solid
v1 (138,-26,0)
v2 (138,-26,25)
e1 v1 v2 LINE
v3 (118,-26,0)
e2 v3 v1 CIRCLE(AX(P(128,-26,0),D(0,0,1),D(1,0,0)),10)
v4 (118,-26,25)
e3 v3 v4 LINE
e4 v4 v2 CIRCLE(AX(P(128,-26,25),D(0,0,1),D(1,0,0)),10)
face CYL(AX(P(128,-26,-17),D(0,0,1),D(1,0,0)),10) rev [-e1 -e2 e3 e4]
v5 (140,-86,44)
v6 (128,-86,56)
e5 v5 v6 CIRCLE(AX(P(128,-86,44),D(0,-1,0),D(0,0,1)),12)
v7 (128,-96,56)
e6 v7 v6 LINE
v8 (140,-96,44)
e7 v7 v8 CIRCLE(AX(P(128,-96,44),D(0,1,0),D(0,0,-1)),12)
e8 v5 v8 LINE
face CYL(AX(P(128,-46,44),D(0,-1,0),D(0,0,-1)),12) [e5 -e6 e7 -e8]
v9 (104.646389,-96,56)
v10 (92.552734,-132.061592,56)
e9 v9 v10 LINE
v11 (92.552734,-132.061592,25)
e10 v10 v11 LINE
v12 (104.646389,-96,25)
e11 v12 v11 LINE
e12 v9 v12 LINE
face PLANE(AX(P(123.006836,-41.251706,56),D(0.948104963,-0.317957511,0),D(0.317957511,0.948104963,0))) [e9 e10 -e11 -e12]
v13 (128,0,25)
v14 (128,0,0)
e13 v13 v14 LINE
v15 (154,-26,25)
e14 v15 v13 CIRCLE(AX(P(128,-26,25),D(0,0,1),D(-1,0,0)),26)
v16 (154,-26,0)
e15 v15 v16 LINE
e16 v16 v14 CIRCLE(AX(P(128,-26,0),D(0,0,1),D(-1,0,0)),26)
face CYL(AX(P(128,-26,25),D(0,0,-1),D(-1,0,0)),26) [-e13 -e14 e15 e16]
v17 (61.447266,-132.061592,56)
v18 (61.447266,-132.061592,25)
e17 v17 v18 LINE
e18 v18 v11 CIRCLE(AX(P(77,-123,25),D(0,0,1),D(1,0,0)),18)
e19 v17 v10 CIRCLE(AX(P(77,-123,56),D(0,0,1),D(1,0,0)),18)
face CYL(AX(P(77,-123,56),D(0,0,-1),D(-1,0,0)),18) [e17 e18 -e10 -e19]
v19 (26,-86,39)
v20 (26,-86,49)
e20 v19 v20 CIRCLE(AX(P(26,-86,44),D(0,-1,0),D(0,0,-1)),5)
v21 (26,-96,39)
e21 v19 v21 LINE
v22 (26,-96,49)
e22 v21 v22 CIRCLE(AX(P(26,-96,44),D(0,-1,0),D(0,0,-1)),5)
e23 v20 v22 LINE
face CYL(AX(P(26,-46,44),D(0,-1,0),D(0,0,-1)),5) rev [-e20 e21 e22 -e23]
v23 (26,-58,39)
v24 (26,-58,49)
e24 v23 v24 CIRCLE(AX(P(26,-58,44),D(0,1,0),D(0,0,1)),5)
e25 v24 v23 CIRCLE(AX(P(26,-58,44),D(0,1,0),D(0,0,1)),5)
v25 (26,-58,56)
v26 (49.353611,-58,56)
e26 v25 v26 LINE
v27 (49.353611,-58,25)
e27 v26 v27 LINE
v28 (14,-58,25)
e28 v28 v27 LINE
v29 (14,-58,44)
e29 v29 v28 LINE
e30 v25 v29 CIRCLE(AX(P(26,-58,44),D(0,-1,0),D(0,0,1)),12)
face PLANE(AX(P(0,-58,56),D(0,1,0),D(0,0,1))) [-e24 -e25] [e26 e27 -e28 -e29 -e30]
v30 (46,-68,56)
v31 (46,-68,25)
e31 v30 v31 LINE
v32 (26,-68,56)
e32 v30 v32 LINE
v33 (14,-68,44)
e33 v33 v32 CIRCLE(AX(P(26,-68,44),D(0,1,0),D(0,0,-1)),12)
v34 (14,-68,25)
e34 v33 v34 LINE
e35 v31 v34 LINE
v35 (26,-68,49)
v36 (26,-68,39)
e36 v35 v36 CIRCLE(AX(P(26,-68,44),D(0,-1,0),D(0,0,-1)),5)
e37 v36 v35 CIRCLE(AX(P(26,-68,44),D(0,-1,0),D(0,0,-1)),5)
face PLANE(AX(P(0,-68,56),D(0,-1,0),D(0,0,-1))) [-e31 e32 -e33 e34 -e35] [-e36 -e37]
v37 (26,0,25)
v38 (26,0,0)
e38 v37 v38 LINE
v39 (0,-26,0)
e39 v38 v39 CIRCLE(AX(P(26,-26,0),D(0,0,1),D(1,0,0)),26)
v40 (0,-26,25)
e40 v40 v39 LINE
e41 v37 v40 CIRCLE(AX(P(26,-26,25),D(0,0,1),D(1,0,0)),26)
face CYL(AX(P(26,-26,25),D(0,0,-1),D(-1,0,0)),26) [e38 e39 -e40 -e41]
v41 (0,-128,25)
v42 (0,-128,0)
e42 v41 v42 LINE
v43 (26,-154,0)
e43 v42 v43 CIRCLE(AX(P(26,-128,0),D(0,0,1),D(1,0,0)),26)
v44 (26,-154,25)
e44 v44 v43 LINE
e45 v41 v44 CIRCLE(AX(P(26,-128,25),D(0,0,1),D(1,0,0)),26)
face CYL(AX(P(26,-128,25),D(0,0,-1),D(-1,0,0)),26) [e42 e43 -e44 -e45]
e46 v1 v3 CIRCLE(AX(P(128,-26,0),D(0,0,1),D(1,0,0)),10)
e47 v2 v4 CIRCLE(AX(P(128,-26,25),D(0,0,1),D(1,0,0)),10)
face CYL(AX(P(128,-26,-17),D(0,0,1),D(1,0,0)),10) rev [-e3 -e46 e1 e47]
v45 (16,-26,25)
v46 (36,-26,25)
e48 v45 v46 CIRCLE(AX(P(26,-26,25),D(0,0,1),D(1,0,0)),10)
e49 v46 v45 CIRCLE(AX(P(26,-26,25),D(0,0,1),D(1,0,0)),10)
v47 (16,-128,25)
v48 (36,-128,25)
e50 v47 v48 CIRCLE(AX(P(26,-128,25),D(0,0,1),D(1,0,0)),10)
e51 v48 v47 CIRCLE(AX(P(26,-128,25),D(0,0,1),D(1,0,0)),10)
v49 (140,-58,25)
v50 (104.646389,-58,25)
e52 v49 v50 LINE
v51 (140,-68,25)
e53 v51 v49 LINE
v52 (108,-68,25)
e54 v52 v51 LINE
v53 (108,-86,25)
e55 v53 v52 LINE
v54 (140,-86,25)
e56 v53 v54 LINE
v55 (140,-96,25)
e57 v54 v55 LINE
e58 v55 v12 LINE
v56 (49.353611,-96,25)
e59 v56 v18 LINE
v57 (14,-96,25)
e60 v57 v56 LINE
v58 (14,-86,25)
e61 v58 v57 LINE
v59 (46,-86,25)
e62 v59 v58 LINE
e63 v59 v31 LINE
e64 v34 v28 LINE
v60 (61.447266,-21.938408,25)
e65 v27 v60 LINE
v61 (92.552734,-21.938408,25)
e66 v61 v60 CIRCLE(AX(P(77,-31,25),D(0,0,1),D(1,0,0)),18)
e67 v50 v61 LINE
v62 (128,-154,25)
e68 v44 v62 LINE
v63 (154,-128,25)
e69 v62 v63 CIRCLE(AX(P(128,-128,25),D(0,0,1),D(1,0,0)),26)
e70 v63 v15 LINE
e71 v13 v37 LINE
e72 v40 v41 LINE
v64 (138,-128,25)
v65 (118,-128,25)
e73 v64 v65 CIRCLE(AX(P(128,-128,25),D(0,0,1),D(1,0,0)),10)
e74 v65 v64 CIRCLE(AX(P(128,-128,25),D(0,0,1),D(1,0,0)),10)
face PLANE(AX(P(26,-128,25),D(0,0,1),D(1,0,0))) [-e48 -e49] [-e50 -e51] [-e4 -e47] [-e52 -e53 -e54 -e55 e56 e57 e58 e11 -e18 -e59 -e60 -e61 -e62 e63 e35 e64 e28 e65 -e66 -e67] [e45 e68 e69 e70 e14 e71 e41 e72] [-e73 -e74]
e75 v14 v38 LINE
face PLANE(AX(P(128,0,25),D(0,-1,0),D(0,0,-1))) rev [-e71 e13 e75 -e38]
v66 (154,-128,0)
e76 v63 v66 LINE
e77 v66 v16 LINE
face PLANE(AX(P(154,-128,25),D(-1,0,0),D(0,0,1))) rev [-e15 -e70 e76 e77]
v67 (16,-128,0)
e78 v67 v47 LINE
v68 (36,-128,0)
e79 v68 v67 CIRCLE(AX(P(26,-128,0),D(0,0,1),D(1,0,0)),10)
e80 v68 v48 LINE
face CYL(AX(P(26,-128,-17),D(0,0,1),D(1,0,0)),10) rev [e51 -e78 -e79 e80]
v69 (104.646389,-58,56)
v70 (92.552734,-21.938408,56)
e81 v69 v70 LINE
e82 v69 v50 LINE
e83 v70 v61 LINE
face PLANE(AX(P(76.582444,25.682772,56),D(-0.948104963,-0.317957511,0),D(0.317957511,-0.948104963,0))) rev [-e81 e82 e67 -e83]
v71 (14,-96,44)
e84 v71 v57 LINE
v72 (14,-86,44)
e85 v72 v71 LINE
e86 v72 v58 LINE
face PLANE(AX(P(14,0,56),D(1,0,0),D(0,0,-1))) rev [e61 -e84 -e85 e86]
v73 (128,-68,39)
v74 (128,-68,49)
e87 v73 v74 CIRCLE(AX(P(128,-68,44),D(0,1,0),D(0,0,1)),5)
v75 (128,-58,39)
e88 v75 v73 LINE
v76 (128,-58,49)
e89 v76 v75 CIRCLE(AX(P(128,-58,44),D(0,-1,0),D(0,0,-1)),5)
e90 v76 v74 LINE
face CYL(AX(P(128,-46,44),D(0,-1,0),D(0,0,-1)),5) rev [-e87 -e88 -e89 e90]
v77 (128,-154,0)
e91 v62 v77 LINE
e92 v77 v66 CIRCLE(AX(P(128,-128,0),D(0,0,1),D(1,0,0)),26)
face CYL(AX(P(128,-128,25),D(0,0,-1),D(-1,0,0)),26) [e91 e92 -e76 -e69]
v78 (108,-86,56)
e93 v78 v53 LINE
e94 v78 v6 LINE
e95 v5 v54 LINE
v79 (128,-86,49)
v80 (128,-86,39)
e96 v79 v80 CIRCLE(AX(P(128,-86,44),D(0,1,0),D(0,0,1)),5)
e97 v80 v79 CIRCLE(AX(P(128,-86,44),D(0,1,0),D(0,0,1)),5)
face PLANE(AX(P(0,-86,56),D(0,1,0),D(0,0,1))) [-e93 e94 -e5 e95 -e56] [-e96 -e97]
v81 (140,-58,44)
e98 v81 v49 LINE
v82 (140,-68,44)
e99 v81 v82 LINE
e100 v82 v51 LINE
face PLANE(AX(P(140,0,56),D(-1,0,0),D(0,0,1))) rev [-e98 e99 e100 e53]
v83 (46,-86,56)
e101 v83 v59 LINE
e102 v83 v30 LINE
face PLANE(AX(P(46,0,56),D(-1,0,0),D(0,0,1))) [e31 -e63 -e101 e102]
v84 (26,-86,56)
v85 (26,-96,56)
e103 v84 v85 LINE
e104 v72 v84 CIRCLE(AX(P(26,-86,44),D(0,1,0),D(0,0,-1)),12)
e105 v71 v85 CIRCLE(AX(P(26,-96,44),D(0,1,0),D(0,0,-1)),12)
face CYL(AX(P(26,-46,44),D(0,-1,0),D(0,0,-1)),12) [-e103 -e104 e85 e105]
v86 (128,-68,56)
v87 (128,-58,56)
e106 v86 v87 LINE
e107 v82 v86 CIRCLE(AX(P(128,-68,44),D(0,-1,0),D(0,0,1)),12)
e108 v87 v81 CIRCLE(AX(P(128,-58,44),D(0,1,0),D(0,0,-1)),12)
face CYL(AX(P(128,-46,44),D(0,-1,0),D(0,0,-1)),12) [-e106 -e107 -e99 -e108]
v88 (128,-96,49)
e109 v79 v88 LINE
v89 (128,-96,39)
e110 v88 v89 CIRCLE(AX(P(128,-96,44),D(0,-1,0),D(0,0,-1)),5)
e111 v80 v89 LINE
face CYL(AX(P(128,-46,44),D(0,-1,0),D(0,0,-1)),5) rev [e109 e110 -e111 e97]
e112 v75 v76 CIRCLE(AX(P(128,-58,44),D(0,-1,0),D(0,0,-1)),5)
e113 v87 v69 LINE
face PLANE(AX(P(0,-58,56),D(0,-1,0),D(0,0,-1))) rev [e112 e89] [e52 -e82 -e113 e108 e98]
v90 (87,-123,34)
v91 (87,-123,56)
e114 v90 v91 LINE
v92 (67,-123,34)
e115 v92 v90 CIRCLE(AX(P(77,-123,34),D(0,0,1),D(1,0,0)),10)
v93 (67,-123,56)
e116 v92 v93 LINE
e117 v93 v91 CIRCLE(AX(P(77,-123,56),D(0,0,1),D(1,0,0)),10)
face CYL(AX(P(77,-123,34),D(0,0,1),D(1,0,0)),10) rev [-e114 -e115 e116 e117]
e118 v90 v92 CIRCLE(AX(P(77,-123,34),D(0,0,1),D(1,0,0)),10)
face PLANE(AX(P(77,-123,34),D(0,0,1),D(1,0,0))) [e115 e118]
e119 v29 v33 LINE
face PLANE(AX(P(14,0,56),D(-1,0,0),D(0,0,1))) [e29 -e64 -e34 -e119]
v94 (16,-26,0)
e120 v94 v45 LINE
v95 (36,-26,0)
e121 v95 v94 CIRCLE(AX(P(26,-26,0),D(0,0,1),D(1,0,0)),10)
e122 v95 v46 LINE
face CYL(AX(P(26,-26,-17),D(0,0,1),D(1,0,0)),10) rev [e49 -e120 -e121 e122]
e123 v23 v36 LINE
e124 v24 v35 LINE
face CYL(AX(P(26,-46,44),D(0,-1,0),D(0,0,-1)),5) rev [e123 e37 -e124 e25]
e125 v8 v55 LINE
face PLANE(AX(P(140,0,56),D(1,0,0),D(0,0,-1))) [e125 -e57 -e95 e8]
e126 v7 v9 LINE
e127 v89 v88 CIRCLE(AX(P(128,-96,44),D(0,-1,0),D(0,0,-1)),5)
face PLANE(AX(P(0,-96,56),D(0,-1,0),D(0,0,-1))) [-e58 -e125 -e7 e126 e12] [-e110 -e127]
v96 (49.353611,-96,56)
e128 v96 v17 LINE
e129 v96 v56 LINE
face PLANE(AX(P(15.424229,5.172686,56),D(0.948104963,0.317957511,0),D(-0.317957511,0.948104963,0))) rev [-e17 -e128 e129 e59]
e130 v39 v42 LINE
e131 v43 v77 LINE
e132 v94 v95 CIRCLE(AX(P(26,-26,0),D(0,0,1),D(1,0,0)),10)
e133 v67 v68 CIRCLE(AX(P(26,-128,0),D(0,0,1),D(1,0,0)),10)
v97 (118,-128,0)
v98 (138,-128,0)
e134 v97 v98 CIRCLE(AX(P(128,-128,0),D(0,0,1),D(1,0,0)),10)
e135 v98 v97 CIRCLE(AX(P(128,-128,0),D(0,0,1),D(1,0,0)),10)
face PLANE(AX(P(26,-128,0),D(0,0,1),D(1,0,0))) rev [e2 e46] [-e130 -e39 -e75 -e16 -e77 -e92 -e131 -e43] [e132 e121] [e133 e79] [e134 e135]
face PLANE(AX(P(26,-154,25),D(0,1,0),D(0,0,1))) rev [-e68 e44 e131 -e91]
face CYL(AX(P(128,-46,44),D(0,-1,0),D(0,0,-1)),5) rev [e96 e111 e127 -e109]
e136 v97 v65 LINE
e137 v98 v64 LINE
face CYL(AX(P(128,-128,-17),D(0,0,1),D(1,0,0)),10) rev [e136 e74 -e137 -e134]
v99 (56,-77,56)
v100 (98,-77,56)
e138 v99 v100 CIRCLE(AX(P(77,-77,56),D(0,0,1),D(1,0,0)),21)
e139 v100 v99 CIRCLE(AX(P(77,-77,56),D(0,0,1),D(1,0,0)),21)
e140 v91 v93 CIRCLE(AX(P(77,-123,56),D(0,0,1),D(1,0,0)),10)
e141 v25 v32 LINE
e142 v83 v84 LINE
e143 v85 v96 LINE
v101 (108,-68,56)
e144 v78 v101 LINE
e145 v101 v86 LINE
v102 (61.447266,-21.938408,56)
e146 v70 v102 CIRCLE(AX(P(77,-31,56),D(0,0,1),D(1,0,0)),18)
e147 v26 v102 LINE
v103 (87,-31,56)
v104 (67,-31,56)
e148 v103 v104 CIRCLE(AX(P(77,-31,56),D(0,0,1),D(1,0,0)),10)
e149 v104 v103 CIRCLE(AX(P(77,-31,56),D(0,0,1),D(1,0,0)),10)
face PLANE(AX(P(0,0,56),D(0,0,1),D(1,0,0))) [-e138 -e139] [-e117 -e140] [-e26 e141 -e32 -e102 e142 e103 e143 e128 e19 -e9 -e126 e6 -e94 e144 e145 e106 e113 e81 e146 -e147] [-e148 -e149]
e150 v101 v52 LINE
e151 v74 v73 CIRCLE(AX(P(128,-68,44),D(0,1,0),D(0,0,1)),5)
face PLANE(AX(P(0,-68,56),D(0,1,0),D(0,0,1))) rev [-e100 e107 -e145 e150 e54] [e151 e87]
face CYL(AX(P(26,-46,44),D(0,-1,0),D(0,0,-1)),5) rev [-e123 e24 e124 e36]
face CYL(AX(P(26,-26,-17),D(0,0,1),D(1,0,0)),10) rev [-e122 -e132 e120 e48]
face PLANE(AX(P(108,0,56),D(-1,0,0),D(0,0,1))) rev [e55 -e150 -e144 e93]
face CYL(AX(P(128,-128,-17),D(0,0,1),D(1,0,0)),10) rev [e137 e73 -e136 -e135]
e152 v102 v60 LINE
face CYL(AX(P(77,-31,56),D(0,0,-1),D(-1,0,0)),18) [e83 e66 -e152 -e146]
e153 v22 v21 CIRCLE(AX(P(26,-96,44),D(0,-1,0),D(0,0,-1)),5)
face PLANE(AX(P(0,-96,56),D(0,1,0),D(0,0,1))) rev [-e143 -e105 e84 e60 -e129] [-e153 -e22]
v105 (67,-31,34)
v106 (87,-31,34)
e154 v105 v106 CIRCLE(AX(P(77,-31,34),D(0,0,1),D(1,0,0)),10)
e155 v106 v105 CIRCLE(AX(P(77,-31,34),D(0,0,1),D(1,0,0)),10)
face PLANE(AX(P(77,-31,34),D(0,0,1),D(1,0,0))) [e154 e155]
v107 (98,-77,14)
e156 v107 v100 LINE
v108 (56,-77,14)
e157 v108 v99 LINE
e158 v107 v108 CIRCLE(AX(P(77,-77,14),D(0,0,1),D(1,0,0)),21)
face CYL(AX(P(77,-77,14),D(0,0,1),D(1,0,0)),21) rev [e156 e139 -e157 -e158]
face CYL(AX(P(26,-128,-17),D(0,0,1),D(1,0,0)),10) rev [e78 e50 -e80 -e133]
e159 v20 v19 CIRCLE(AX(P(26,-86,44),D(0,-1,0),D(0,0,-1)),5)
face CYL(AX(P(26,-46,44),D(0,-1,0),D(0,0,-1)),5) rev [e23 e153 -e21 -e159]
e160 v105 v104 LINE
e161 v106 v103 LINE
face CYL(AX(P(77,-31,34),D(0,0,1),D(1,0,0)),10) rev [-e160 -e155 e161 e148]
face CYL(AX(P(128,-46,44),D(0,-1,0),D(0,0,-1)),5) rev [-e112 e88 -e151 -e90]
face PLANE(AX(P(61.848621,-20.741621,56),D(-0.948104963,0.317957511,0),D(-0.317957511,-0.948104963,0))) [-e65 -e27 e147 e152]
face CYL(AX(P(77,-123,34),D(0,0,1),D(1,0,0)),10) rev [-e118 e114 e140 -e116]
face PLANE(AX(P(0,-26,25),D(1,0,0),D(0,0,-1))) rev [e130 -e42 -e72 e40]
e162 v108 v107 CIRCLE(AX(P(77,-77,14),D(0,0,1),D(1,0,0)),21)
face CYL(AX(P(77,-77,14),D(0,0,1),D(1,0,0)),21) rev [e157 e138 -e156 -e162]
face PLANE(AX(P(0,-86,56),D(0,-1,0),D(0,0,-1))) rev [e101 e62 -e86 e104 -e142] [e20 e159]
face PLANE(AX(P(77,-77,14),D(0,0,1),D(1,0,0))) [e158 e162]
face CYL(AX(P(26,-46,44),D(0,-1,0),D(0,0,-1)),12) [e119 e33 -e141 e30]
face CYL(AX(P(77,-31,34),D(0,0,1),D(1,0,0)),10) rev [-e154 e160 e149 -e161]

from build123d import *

# Parameters (mm, degrees)
BASE_PLATE_DEPTH         = 25
FLANGE_BOSS_DEPTH        = 31
LUG_SLOT_1_DEPTH         = 50
LUG_SLOT_2_DEPTH         = 50
LUG_PIN_HOLES_SKETCH_R   = 5
LUG_PIN_HOLES_2X_DEPTH   = 50
FLANGE_HOLES_SKETCH_R    = 10
FLANGE_HOLES_2X_DEPTH    = 22
CENTRE_BORE_SKETCH_R     = 21
CENTRE_BORE_42_DEPTH     = 42
CORNER_HOLES_SKETCH_R    = 10
CORNER_HOLES_4X_20_DEPTH = 42


with BuildPart() as part:
    # Base Plate Sketch → Base Plate (new body)
    with BuildSketch(Plane.XY):
        with BuildLine():
            Line((0, -26), (0, -128))
            ThreePointArc((0, -128), (7.615223689, -146.384776311), (26, -154))
            Line((26, -154), (128, -154))
            ThreePointArc((128, -154), (146.384776311, -146.384776311), (154, -128))
            Line((154, -128), (154, -26))
            ThreePointArc((154, -26), (146.384776311, -7.615223689), (128, 0))
            Line((128, 0), (26, 0))
            ThreePointArc((26, 0), (7.615223689, -7.615223689), (0, -26))
        make_face()
    extrude(amount=BASE_PLATE_DEPTH)

    # Flange Boss Sketch → Flange Boss (add)
    with BuildSketch(Plane.XY.offset(25)):
        with BuildLine():
            Line((14, -96), (49.353610872, -96))
            Line((49.353610872, -96), (61.447265664, -132.061592281))
            ThreePointArc((61.447265664, -132.061592281), (77, -141), (92.552734336, -132.061592281))
            Line((92.552734336, -132.061592281), (104.646389128, -96))
            Line((104.646389128, -96), (140, -96))
            Line((140, -96), (140, -86))
            Line((140, -86), (108, -86))
            Line((108, -86), (108, -68))
            Line((108, -68), (140, -68))
            Line((140, -68), (140, -58))
            Line((140, -58), (104.646389128, -58))
            Line((104.646389128, -58), (92.552734336, -21.938407719))
            ThreePointArc((92.552734336, -21.938407719), (77, -13), (61.447265664, -21.938407719))
            Line((61.447265664, -21.938407719), (49.353610872, -58))
            Line((49.353610872, -58), (14, -58))
            Line((14, -58), (14, -68))
            Line((14, -68), (46, -68))
            Line((46, -68), (46, -77))
            Line((46, -77), (46, -86))
            Line((46, -86), (14, -86))
            Line((14, -86), (14, -96))
        make_face()
    extrude(amount=FLANGE_BOSS_DEPTH)

    # Lug Slot 1 Sketch → Lug Slot 1 (cut)
    with BuildSketch(Plane.XZ.offset(96)):
        with BuildLine():
            Line((140, 56), (140, 44))
            ThreePointArc((140, 44), (136.485281374, 52.485281374), (128, 56))
            Line((128, 56), (140, 56))
        make_face()
    extrude(amount=-LUG_SLOT_1_DEPTH, mode=Mode.SUBTRACT)

    # Lug Slot 2 Sketch → Lug Slot 2 (cut)
    with BuildSketch(Plane.XZ.offset(96)):
        with BuildLine():
            Line((14, 56), (26, 56))
            ThreePointArc((26, 56), (17.514718626, 52.485281374), (14, 44))
            Line((14, 44), (14, 56))
        make_face()
    extrude(amount=-LUG_SLOT_2_DEPTH, mode=Mode.SUBTRACT)

    # Lug Pin Holes Sketch → Lug Pin Holes 2x (cut)
    with BuildSketch(Plane.XZ.offset(96)):
        with Locations(Location((128, 44, 0), (0, 0, 270))):
            Circle(LUG_PIN_HOLES_SKETCH_R)
        with Locations(Location((26, 44, 0), (0, 0, 270))):
            Circle(LUG_PIN_HOLES_SKETCH_R)
    extrude(amount=-LUG_PIN_HOLES_2X_DEPTH, mode=Mode.SUBTRACT)

    # Flange Holes Sketch → Flange Holes 2x (cut)
    with BuildSketch(Plane.XY.offset(56)):
        with Locations((77, -31)):
            Circle(FLANGE_HOLES_SKETCH_R)
        with Locations((77, -123)):
            Circle(FLANGE_HOLES_SKETCH_R)
    extrude(amount=-FLANGE_HOLES_2X_DEPTH, mode=Mode.SUBTRACT)

    # Centre Bore Sketch → Centre Bore Ø42 (cut)
    with BuildSketch(Plane.XY.offset(56)):
        with Locations((77, -77)):
            Circle(CENTRE_BORE_SKETCH_R)
    extrude(amount=-CENTRE_BORE_42_DEPTH, mode=Mode.SUBTRACT)

    # Corner Holes Sketch → Corner Holes 4xØ20 (cut)
    with BuildSketch(Plane.XY.offset(25)):
        with Locations((26, -26)):
            Circle(CORNER_HOLES_SKETCH_R)
        with Locations((128, -26)):
            Circle(CORNER_HOLES_SKETCH_R)
        with Locations((128, -128)):
            Circle(CORNER_HOLES_SKETCH_R)
        with Locations((26, -128)):
            Circle(CORNER_HOLES_SKETCH_R)
    extrude(amount=-CORNER_HOLES_4X_20_DEPTH, mode=Mode.SUBTRACT)


solid = part.part
